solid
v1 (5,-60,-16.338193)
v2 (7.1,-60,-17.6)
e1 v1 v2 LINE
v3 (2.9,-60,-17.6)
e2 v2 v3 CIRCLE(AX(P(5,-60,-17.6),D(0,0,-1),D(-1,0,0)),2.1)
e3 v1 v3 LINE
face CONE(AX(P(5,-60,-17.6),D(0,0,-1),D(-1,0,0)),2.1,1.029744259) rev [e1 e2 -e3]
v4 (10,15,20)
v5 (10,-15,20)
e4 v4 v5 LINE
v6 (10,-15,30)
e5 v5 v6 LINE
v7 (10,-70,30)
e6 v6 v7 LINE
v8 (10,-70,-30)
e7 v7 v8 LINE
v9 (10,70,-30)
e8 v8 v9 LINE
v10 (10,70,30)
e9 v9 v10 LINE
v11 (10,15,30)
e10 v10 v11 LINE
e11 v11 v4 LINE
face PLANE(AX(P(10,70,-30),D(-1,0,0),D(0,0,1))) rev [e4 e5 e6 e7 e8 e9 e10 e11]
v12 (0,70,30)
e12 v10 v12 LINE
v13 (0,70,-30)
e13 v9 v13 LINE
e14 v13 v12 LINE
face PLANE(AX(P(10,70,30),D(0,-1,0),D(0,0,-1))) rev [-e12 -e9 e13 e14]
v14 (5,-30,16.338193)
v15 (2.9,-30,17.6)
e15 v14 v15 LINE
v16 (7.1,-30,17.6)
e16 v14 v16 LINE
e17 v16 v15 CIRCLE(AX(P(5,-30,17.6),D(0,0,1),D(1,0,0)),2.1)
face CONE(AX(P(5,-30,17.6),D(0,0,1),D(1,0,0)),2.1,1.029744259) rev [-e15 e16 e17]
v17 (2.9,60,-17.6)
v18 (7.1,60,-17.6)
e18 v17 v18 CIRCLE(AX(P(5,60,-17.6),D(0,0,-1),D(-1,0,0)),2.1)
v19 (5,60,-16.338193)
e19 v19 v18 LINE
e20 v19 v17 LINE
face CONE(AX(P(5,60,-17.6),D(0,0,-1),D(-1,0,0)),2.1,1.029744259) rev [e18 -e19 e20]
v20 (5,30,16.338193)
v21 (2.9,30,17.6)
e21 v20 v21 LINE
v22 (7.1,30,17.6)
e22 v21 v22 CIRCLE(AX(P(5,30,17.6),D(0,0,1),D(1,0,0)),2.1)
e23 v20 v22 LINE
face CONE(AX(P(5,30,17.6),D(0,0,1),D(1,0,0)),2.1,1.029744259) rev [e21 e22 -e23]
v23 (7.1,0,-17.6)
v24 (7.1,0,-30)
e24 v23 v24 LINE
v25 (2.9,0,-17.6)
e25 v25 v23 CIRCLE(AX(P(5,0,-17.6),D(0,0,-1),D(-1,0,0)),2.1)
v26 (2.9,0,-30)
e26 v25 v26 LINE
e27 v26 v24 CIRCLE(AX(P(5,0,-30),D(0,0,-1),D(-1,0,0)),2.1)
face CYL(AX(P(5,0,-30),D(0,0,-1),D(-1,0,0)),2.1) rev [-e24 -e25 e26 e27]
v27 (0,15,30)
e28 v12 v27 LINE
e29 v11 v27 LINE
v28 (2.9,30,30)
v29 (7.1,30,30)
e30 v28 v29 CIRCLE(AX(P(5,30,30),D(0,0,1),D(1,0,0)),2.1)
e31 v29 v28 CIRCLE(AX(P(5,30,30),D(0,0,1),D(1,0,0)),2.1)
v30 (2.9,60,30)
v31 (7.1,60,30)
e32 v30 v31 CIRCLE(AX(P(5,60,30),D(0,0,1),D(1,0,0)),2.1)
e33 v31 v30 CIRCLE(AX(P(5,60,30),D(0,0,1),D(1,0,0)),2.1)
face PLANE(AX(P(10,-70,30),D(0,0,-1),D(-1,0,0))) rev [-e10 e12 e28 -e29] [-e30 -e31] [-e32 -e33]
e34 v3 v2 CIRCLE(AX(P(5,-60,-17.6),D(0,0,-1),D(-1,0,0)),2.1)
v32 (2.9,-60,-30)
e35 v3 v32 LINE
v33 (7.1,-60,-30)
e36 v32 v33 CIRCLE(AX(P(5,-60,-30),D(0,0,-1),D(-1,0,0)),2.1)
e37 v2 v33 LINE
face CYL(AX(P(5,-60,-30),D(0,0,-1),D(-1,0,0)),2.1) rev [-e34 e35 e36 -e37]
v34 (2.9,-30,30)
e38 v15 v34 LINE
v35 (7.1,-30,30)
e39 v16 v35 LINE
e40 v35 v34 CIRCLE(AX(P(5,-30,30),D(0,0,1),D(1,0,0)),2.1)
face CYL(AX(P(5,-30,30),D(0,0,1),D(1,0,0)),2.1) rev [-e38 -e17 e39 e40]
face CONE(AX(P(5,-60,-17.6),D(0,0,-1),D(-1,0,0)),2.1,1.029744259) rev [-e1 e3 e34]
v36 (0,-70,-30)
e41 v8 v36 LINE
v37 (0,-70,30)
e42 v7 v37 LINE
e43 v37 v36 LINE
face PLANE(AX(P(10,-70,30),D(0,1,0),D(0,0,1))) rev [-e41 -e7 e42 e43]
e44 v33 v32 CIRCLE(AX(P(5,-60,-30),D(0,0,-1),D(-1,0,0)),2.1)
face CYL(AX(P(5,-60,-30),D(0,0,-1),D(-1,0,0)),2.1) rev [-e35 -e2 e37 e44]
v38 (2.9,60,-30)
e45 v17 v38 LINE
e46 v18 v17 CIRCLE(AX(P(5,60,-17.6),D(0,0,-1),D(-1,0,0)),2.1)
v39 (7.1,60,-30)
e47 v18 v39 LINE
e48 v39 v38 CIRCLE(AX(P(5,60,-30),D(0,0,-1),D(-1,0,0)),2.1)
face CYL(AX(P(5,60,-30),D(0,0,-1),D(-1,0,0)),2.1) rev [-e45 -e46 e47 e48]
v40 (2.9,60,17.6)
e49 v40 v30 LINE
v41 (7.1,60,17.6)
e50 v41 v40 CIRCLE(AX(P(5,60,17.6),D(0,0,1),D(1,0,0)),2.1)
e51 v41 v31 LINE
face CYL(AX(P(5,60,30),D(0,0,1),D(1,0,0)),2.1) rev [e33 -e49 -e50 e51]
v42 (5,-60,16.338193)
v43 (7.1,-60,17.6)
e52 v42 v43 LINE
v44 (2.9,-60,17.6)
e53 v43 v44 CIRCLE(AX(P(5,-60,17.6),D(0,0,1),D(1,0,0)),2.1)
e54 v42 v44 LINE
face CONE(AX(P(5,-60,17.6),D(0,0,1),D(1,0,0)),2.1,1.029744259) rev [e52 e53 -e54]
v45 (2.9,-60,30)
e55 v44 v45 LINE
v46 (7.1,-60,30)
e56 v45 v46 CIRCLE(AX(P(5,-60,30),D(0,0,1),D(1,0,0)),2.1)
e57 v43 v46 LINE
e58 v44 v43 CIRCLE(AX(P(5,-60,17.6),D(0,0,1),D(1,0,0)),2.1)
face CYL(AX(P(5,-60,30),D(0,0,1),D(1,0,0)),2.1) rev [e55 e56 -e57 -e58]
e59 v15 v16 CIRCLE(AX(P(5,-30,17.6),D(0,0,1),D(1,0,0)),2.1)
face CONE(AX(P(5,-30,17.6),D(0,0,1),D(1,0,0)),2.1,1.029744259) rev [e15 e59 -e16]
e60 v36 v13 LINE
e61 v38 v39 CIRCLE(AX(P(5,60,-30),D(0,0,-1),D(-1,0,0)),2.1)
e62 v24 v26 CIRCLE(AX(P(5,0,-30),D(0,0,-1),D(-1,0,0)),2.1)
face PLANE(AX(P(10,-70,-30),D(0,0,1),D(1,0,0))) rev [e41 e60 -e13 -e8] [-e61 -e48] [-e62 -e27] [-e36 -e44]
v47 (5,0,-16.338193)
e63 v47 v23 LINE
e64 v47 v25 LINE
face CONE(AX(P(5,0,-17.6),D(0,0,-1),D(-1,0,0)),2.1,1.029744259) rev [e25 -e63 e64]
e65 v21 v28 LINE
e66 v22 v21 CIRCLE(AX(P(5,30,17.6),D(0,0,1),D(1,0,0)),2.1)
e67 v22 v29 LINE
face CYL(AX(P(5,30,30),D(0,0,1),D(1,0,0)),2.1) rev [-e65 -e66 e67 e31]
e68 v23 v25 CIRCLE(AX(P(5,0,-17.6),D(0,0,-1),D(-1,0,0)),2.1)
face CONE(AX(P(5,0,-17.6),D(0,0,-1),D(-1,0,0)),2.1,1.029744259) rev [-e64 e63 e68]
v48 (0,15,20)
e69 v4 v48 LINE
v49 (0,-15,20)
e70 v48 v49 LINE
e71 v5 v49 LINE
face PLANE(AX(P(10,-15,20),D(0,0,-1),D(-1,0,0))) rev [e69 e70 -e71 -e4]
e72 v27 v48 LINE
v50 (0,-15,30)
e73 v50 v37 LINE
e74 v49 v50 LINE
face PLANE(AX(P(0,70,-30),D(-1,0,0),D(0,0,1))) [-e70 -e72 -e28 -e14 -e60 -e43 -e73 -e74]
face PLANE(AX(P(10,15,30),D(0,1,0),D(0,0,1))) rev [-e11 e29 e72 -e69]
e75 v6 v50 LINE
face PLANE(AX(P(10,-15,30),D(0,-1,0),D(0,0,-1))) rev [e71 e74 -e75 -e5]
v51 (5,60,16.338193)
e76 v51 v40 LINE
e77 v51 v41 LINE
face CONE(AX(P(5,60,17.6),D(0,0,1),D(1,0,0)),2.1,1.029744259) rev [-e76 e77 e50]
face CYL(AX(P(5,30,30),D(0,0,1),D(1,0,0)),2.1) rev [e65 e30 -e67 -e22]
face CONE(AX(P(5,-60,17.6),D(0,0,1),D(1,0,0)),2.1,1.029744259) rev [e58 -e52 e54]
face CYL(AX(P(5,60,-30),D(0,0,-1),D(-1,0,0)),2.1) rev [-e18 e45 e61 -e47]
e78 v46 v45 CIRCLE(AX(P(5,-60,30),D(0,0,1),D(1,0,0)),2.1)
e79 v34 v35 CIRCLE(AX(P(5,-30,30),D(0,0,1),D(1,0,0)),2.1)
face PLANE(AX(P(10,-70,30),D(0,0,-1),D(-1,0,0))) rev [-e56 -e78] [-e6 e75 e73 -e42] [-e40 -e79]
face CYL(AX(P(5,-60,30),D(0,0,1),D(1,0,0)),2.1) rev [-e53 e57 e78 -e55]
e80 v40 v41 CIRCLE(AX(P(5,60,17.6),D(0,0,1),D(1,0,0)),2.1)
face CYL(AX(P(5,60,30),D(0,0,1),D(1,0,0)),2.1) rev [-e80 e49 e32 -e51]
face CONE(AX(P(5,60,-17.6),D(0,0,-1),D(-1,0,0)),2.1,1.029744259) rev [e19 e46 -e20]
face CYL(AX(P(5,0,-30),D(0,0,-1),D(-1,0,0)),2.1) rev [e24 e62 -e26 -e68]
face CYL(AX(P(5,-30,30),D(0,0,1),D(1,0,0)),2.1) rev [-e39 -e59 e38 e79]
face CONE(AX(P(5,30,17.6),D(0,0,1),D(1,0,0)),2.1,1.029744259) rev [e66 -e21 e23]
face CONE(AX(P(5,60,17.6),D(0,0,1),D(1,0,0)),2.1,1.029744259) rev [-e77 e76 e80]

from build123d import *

# Parameters (mm, degrees)
SKETCH_1_W             = 60
SKETCH_1_H             = 140
BOSS_EXTRUDE_1_DEPTH   = 10
SKETCH_4_W             = 10
SKETCH_4_H             = 30
CUT_EXTRUDE_1_DEPTH    = 77.811457479
LINEAR_PATTERN_2_COUNT = 3
LINEAR_PATTERN_2_PITCH = 60
M5_TAPPED_HOLE_3_D     = 4.2
M5_TAPPED_HOLE_3_DEPTH = 12.4
M5_TAPPED_HOLE_3_TIP   = 1.2618073


with BuildPart() as part:
    # Sketch 1 → Boss-Extrude 1 (new body)
    with BuildSketch(Plane(origin=(0, 0, 0), x_dir=(0, 0, -1), z_dir=(1, 0, 0))):
        Rectangle(SKETCH_1_W, SKETCH_1_H)
    extrude(amount=BOSS_EXTRUDE_1_DEPTH)

    # Sketch 4 → Cut-Extrude 1 (cut, through all)
    with BuildSketch(Plane.ZY):
        with Locations((25, 0)):
            Rectangle(SKETCH_4_W, SKETCH_4_H)
    extrude(amount=-CUT_EXTRUDE_1_DEPTH, mode=Mode.SUBTRACT)

    # Sketch 5 → M5 Tapped Hole 2 (revolve, cut)
    with BuildSketch(Plane(origin=(5, 60, -30), x_dir=(0, 1, 0), z_dir=(1, 0, 0))):
        Polygon((0, 0), (0, 13.6618073), (2.1, 12.4), (2.1, 0), align=None)
    m5_tapped_hole_2 = revolve(axis=Axis((5, 60, -36.35), (0, 0, 1)), mode=Mode.SUBTRACT)

    # Linear Pattern 2: M5 Tapped Hole 2 ×3
    with Locations(*[(0, -i * LINEAR_PATTERN_2_PITCH, 0) for i in range(1, LINEAR_PATTERN_2_COUNT)]):
        add(m5_tapped_hole_2, mode=Mode.SUBTRACT)

    # M5 Tapped Hole 3
    with Locations(Plane.XY.offset(30)):
        with Locations((5, -60), (5, -30), (5, 30), (5, 60)):
            Hole(M5_TAPPED_HOLE_3_D / 2, depth=M5_TAPPED_HOLE_3_DEPTH)
            with Locations((0, 0, -(M5_TAPPED_HOLE_3_DEPTH + M5_TAPPED_HOLE_3_TIP / 2))):  # 118° drill point
                Cone(0, M5_TAPPED_HOLE_3_D / 2, M5_TAPPED_HOLE_3_TIP, mode=Mode.SUBTRACT)


solid = part.part
